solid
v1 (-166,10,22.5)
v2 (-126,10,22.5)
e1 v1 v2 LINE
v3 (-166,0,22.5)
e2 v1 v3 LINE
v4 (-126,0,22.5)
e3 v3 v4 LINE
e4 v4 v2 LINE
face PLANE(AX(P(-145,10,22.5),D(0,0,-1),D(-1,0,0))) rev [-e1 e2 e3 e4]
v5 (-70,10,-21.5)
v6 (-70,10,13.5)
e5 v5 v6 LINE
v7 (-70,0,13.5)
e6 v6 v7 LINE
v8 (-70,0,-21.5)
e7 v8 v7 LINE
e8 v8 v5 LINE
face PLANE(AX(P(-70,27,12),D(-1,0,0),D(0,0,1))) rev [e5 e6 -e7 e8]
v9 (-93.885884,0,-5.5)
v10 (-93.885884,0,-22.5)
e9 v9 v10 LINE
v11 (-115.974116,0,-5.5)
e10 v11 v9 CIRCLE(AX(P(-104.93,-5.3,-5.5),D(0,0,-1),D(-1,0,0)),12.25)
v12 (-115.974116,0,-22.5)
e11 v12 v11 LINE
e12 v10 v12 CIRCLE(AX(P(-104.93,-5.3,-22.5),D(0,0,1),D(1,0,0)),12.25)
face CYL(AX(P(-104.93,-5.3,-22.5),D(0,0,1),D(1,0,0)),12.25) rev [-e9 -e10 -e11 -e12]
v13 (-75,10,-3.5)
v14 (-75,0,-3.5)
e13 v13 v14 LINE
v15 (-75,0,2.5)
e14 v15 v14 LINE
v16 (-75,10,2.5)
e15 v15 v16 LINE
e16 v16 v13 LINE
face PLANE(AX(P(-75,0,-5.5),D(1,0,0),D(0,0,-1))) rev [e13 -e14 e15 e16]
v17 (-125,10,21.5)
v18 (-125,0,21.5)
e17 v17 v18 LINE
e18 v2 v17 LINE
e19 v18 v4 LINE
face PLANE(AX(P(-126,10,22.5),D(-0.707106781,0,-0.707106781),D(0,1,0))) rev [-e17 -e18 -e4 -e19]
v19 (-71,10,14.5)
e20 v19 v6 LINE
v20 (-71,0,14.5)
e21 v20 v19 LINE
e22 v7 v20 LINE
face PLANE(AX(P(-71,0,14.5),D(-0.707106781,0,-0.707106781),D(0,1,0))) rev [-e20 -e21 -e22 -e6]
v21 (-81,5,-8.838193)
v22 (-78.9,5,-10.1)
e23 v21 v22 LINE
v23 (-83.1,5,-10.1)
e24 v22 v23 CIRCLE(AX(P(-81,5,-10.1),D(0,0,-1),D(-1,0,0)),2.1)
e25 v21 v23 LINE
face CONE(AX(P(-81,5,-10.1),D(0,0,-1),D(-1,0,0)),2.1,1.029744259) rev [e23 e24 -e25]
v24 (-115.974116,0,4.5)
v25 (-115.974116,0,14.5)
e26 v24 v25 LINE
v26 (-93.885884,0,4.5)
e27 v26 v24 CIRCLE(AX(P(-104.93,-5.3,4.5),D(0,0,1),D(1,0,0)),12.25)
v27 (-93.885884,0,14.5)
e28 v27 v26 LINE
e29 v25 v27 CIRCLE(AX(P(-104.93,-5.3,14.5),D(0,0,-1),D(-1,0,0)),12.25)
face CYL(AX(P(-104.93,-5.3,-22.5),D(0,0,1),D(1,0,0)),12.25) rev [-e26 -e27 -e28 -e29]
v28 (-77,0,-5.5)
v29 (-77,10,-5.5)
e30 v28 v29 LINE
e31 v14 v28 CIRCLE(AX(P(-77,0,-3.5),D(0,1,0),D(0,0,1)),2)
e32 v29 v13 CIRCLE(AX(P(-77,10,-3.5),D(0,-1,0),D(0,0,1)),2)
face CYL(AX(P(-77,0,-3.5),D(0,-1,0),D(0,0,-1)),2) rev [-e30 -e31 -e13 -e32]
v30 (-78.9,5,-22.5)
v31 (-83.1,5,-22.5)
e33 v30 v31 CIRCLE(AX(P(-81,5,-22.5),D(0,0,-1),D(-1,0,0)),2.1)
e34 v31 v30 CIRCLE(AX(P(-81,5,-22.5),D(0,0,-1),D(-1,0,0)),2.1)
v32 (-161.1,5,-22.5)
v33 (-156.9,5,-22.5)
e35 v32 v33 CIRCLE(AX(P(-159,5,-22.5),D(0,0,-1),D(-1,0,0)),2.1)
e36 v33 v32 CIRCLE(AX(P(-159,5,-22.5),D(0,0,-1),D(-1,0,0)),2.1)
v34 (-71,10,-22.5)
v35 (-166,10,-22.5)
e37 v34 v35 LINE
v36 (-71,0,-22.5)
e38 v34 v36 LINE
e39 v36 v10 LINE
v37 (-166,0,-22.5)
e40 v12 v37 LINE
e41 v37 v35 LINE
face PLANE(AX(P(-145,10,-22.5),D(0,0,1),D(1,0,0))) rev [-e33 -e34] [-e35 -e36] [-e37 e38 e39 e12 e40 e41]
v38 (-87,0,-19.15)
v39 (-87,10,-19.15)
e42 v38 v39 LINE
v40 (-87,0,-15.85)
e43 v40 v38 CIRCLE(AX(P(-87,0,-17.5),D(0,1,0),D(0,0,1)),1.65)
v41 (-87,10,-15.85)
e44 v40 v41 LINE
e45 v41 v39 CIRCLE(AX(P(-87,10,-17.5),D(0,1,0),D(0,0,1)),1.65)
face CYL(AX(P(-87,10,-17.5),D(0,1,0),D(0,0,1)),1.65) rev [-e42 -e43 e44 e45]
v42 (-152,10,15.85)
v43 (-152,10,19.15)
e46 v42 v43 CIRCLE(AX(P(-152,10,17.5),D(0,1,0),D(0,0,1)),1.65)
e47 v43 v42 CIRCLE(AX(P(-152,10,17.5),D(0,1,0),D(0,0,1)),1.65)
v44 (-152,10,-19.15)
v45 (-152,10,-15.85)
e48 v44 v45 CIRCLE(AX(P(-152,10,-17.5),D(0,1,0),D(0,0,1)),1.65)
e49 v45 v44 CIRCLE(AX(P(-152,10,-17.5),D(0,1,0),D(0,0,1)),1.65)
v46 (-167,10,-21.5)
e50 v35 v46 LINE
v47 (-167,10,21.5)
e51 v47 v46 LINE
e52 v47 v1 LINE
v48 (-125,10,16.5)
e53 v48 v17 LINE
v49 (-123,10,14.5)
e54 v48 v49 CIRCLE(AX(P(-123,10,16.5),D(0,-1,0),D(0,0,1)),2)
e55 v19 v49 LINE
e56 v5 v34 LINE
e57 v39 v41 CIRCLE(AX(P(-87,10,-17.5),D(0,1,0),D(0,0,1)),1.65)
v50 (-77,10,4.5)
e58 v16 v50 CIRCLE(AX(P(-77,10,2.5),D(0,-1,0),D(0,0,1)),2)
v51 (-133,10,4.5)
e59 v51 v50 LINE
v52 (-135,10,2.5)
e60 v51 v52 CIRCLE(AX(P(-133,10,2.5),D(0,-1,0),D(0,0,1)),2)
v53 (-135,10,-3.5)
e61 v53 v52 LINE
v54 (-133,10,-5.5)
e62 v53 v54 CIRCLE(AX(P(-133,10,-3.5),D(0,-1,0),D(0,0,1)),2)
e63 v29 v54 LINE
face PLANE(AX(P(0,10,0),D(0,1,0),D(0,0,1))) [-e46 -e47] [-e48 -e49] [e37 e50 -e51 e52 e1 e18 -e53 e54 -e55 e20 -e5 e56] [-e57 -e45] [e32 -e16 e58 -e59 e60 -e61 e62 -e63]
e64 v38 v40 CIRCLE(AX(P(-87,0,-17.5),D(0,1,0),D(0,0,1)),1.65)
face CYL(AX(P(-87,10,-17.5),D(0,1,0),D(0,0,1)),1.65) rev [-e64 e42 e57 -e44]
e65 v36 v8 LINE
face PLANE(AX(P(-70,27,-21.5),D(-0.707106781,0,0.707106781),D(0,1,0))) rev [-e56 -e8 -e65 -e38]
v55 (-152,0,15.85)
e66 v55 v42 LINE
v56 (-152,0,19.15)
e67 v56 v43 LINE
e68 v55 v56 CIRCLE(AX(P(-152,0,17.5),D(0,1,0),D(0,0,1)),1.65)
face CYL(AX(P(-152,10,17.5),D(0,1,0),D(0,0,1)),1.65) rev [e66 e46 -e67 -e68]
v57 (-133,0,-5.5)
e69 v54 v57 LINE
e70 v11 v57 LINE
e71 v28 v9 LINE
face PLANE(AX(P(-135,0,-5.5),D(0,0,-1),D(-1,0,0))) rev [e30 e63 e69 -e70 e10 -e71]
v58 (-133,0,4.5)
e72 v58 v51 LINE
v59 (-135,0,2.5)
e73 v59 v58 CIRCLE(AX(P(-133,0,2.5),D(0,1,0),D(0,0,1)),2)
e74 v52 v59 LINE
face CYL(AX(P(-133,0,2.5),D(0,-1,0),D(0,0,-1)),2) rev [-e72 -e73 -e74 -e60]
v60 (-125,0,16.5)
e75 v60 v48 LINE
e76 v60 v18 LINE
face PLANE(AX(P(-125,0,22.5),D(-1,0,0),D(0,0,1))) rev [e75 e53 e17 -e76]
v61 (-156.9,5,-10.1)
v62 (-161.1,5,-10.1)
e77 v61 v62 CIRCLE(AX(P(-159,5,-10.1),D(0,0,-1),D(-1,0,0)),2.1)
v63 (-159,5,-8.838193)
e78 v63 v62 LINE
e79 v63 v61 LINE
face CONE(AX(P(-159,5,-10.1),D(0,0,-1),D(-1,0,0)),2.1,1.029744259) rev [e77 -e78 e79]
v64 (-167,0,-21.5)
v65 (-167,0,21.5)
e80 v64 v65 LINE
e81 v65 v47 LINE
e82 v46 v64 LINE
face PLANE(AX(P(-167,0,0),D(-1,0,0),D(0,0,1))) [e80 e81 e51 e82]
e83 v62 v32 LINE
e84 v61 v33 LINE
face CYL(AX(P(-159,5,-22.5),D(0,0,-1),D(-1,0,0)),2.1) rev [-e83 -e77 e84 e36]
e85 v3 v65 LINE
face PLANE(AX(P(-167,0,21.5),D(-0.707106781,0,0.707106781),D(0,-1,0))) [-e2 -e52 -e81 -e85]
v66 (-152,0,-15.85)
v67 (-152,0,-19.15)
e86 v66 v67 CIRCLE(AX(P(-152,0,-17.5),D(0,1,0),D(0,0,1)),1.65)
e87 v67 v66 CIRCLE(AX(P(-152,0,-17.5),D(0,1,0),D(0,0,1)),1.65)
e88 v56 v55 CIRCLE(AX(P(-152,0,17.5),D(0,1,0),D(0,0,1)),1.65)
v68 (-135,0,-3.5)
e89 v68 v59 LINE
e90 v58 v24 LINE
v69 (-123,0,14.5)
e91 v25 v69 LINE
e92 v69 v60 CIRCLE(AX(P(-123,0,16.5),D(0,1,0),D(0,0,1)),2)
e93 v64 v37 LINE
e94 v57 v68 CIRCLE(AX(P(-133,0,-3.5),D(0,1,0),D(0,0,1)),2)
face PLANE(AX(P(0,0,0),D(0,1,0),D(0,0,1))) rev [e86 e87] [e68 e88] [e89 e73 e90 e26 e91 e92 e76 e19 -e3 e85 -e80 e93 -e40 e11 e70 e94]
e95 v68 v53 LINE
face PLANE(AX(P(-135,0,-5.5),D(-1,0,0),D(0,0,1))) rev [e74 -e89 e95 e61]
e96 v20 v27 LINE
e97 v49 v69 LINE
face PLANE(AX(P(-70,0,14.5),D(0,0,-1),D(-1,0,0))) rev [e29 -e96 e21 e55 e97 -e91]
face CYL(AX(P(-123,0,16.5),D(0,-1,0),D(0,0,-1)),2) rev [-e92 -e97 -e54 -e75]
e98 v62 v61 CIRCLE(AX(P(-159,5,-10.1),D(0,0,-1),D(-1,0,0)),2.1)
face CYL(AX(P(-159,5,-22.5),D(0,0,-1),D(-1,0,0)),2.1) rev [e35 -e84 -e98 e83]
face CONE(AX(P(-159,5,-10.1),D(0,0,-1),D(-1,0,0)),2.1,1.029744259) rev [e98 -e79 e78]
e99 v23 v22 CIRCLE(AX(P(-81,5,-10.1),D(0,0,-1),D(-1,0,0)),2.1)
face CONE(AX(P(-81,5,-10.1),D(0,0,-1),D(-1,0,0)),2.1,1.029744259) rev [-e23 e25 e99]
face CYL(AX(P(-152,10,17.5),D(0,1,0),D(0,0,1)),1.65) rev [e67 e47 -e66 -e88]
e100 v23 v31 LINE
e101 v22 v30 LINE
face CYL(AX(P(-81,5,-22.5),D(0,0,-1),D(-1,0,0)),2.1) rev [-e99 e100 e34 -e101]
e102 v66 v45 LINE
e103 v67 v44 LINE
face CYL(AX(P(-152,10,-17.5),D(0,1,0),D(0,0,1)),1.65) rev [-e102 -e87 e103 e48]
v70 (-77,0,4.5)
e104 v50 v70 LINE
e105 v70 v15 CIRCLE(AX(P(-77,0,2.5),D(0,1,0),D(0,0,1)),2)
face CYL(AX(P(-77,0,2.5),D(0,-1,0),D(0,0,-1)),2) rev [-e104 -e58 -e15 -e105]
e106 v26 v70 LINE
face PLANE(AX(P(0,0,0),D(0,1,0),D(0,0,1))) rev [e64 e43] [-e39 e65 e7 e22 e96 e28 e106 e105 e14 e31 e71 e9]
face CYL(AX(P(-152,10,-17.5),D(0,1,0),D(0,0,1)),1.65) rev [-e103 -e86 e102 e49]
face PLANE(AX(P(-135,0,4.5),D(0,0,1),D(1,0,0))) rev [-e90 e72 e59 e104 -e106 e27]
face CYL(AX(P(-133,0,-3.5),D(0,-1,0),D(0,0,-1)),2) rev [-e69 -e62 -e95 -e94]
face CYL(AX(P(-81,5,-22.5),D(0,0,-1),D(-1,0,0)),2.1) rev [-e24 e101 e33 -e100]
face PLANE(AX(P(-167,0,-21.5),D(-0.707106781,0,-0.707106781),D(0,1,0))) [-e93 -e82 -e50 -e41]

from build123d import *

# Parameters (mm, degrees)
SKETCH1_W             = 290
SKETCH1_H             = 45
BOSS_EXTRUDE1_DEPTH   = 10
SKETCH3_W             = 60
SKETCH3_H             = 10
CUT_EXTRUDE2_DEPTH    = 10
SKETCH4_W             = 45
SKETCH4_H             = 10
BOSS_EXTRUDE2_DEPTH   = 22
SKETCH6_R             = 5
CUT_EXTRUDE4_DEPTH    = 30
SKETCH7_W             = 80
SKETCH7_H             = 25
CUT_EXTRUDE5_DEPTH    = 27
SKETCH9_W             = 80
SKETCH9_H             = 45
CUT_EXTRUDE7_DEPTH    = 42
CUT_EXTRUDE8_DEPTH    = 20
SKETCH13_W            = 223.21076669
SKETCH13_H            = 10
CUT_EXTRUDE11_DEPTH   = 105
M5_TAPPED_HOLE1_D     = 4.2
M5_TAPPED_HOLE1_DEPTH = 12.4
M5_TAPPED_HOLE1_TIP   = 1.2618073
SKETCH19_W            = 55
SKETCH19_H            = 8
CUT_EXTRUDE13_DEPTH   = 169.805361289
SKETCH20_R            = 12.25
CUT_EXTRUDE14_DEPTH   = 174.245490562
M4_TAPPED_HOLE1_D     = 3.3
M4_TAPPED_HOLE1_DEPTH = 10.1
M4_TAPPED_HOLE1_TIP   = 0.991420021
CHAMFER1_SIZE         = 1
FILLET1_R             = 2
FILLET2_R             = 2


with BuildPart() as part:
    # Sketch1 → Boss-Extrude1 (new body)
    with BuildSketch(Plane(origin=(0, 0, 0), x_dir=(1, 0, 0), z_dir=(0, 1, 0))):
        Rectangle(SKETCH1_W, SKETCH1_H)
    extrude(amount=BOSS_EXTRUDE1_DEPTH)

    # Sketch3 → Cut-Extrude2 (cut)
    with BuildSketch(Plane(origin=(0, 10, 0), x_dir=(1, 0, 0), z_dir=(0, 1, 0))):
        with Locations((-105, 0.5)):
            Rectangle(SKETCH3_W, SKETCH3_H)
    extrude(amount=-CUT_EXTRUDE2_DEPTH, mode=Mode.SUBTRACT)

    # Sketch4 → Boss-Extrude2 (add)
    with BuildSketch(Plane.ZY.offset(145)):
        with Locations((0, 5)):
            Rectangle(SKETCH4_W, SKETCH4_H)
    extrude(amount=BOSS_EXTRUDE2_DEPTH)

    # Sketch6 → Cut-Extrude4 (cut)
    with BuildSketch(Plane(origin=(0, 10, 0), x_dir=(1, 0, 0), z_dir=(0, 1, 0))):
        with Locations(Location((-10, 0.5, 0), (0, 0, 270))):
            Circle(SKETCH6_R)
        with Locations(Location((-50, 0.5, 0), (0, 0, 270))):
            Circle(SKETCH6_R)
    extrude(amount=-CUT_EXTRUDE4_DEPTH, mode=Mode.SUBTRACT)

    # Sketch7 → Cut-Extrude5 (cut)
    with BuildSketch(Plane.XZ):
        with Locations((-30, -0.5)):
            Rectangle(SKETCH7_W, SKETCH7_H)
    extrude(amount=-CUT_EXTRUDE5_DEPTH, mode=Mode.SUBTRACT)

    # Sketch9 → Cut-Extrude7 (cut)
    with BuildSketch(Plane(origin=(0, 10, 0), x_dir=(1, 0, 0), z_dir=(0, 1, 0))):
        with Locations((-30, 0)):
            Rectangle(SKETCH9_W, SKETCH9_H)
    extrude(amount=-CUT_EXTRUDE7_DEPTH, mode=Mode.SUBTRACT)


with BuildPart() as cut_extrude7_piece_1:
    # of the separate pieces the step leaves, piece 1, a body of its own (cut_extrude7_pieces)
    add(part.part.solids().sort_by_distance((145, 0, -22.5))[0])

    # Sketch10 → Cut-Extrude8 (cut)
    with BuildSketch(Plane.XY.offset(22.5)):
        Polygon((145, 0), (145, 5), (130, 0), align=None)
    extrude(amount=-CUT_EXTRUDE8_DEPTH, mode=Mode.SUBTRACT)

    # Sketch13 → Cut-Extrude11 (cut)
    with BuildSketch(Plane.XY.offset(22.5)):
        with Locations((41.605383345, 5)):
            Rectangle(SKETCH13_W, SKETCH13_H)
    extrude(amount=-CUT_EXTRUDE11_DEPTH, mode=Mode.SUBTRACT)


with BuildPart() as cut_extrude7_piece_2:
    # of the separate pieces the step leaves, piece 2, a body of its own (cut_extrude7_pieces)
    add(part.part.solids().sort_by_distance((-70, 10, -22.5))[0])

    # M5 Tapped Hole1
    with Locations(Plane(origin=(-159, 5, -22.5), x_dir=(-1, 0, 0), z_dir=(0, 0, -1))):
        with Locations((0, 0), (-78, 0)):
            Hole(M5_TAPPED_HOLE1_D / 2, depth=M5_TAPPED_HOLE1_DEPTH)
            with Locations((0, 0, -(M5_TAPPED_HOLE1_DEPTH + M5_TAPPED_HOLE1_TIP / 2))):  # 118° drill point
                Cone(0, M5_TAPPED_HOLE1_D / 2, M5_TAPPED_HOLE1_TIP, mode=Mode.SUBTRACT)

    # Sketch19 → Cut-Extrude13 (cut, through all)
    with BuildSketch(Plane(origin=(0, 10, 0), x_dir=(1, 0, 0), z_dir=(0, 1, 0))):
        with Locations((-97.5, -18.5)):
            Rectangle(SKETCH19_W, SKETCH19_H)
    extrude(amount=-CUT_EXTRUDE13_DEPTH, mode=Mode.SUBTRACT)

    # Sketch20 → Cut-Extrude14 (cut, through all)
    with BuildSketch(Plane.XY.offset(22.5)):
        with Locations((-104.93, -5.3)):
            Circle(SKETCH20_R)
    extrude(amount=-CUT_EXTRUDE14_DEPTH, mode=Mode.SUBTRACT)

    # M4 Tapped Hole1
    with Locations(Plane(origin=(-152, 10, -17.5), x_dir=(0, 0, 1), z_dir=(0, 1, 0))):
        with Locations((0, 0), (0, 65), (35, 0)):
            Hole(M4_TAPPED_HOLE1_D / 2, depth=M4_TAPPED_HOLE1_DEPTH)
            with Locations((0, 0, -(M4_TAPPED_HOLE1_DEPTH + M4_TAPPED_HOLE1_TIP / 2))):  # 118° drill point
                Cone(0, M4_TAPPED_HOLE1_D / 2, M4_TAPPED_HOLE1_TIP, mode=Mode.SUBTRACT)

    # Chamfer1
    chamfer1_edges = [cut_extrude7_piece_2.edges().sort_by_distance(p)[0] for p in [
        (-167, 5, -22.5),
        (-167, 5, 22.5),
        (-70, 5, 14.5),
        (-125, 5, 22.5),
        (-70, 5, -22.5),
    ]]
    chamfer(chamfer1_edges, length=CHAMFER1_SIZE)

    # Fillet1
    fillet1_edges = [cut_extrude7_piece_2.edges().sort_by_distance(p)[0] for p in [
        (-125, 5, 14.5),
    ]]
    fillet(fillet1_edges, radius=FILLET1_R)

    # Fillet2
    fillet2_edges = [cut_extrude7_piece_2.edges().sort_by_distance(p)[0] for p in [
        (-75, 5, 4.5),
        (-135, 5, 4.5),
        (-135, 5, -5.5),
        (-75, 5, -5.5),
    ]]
    fillet(fillet2_edges, radius=FILLET2_R)


solid = cut_extrude7_piece_2.part
